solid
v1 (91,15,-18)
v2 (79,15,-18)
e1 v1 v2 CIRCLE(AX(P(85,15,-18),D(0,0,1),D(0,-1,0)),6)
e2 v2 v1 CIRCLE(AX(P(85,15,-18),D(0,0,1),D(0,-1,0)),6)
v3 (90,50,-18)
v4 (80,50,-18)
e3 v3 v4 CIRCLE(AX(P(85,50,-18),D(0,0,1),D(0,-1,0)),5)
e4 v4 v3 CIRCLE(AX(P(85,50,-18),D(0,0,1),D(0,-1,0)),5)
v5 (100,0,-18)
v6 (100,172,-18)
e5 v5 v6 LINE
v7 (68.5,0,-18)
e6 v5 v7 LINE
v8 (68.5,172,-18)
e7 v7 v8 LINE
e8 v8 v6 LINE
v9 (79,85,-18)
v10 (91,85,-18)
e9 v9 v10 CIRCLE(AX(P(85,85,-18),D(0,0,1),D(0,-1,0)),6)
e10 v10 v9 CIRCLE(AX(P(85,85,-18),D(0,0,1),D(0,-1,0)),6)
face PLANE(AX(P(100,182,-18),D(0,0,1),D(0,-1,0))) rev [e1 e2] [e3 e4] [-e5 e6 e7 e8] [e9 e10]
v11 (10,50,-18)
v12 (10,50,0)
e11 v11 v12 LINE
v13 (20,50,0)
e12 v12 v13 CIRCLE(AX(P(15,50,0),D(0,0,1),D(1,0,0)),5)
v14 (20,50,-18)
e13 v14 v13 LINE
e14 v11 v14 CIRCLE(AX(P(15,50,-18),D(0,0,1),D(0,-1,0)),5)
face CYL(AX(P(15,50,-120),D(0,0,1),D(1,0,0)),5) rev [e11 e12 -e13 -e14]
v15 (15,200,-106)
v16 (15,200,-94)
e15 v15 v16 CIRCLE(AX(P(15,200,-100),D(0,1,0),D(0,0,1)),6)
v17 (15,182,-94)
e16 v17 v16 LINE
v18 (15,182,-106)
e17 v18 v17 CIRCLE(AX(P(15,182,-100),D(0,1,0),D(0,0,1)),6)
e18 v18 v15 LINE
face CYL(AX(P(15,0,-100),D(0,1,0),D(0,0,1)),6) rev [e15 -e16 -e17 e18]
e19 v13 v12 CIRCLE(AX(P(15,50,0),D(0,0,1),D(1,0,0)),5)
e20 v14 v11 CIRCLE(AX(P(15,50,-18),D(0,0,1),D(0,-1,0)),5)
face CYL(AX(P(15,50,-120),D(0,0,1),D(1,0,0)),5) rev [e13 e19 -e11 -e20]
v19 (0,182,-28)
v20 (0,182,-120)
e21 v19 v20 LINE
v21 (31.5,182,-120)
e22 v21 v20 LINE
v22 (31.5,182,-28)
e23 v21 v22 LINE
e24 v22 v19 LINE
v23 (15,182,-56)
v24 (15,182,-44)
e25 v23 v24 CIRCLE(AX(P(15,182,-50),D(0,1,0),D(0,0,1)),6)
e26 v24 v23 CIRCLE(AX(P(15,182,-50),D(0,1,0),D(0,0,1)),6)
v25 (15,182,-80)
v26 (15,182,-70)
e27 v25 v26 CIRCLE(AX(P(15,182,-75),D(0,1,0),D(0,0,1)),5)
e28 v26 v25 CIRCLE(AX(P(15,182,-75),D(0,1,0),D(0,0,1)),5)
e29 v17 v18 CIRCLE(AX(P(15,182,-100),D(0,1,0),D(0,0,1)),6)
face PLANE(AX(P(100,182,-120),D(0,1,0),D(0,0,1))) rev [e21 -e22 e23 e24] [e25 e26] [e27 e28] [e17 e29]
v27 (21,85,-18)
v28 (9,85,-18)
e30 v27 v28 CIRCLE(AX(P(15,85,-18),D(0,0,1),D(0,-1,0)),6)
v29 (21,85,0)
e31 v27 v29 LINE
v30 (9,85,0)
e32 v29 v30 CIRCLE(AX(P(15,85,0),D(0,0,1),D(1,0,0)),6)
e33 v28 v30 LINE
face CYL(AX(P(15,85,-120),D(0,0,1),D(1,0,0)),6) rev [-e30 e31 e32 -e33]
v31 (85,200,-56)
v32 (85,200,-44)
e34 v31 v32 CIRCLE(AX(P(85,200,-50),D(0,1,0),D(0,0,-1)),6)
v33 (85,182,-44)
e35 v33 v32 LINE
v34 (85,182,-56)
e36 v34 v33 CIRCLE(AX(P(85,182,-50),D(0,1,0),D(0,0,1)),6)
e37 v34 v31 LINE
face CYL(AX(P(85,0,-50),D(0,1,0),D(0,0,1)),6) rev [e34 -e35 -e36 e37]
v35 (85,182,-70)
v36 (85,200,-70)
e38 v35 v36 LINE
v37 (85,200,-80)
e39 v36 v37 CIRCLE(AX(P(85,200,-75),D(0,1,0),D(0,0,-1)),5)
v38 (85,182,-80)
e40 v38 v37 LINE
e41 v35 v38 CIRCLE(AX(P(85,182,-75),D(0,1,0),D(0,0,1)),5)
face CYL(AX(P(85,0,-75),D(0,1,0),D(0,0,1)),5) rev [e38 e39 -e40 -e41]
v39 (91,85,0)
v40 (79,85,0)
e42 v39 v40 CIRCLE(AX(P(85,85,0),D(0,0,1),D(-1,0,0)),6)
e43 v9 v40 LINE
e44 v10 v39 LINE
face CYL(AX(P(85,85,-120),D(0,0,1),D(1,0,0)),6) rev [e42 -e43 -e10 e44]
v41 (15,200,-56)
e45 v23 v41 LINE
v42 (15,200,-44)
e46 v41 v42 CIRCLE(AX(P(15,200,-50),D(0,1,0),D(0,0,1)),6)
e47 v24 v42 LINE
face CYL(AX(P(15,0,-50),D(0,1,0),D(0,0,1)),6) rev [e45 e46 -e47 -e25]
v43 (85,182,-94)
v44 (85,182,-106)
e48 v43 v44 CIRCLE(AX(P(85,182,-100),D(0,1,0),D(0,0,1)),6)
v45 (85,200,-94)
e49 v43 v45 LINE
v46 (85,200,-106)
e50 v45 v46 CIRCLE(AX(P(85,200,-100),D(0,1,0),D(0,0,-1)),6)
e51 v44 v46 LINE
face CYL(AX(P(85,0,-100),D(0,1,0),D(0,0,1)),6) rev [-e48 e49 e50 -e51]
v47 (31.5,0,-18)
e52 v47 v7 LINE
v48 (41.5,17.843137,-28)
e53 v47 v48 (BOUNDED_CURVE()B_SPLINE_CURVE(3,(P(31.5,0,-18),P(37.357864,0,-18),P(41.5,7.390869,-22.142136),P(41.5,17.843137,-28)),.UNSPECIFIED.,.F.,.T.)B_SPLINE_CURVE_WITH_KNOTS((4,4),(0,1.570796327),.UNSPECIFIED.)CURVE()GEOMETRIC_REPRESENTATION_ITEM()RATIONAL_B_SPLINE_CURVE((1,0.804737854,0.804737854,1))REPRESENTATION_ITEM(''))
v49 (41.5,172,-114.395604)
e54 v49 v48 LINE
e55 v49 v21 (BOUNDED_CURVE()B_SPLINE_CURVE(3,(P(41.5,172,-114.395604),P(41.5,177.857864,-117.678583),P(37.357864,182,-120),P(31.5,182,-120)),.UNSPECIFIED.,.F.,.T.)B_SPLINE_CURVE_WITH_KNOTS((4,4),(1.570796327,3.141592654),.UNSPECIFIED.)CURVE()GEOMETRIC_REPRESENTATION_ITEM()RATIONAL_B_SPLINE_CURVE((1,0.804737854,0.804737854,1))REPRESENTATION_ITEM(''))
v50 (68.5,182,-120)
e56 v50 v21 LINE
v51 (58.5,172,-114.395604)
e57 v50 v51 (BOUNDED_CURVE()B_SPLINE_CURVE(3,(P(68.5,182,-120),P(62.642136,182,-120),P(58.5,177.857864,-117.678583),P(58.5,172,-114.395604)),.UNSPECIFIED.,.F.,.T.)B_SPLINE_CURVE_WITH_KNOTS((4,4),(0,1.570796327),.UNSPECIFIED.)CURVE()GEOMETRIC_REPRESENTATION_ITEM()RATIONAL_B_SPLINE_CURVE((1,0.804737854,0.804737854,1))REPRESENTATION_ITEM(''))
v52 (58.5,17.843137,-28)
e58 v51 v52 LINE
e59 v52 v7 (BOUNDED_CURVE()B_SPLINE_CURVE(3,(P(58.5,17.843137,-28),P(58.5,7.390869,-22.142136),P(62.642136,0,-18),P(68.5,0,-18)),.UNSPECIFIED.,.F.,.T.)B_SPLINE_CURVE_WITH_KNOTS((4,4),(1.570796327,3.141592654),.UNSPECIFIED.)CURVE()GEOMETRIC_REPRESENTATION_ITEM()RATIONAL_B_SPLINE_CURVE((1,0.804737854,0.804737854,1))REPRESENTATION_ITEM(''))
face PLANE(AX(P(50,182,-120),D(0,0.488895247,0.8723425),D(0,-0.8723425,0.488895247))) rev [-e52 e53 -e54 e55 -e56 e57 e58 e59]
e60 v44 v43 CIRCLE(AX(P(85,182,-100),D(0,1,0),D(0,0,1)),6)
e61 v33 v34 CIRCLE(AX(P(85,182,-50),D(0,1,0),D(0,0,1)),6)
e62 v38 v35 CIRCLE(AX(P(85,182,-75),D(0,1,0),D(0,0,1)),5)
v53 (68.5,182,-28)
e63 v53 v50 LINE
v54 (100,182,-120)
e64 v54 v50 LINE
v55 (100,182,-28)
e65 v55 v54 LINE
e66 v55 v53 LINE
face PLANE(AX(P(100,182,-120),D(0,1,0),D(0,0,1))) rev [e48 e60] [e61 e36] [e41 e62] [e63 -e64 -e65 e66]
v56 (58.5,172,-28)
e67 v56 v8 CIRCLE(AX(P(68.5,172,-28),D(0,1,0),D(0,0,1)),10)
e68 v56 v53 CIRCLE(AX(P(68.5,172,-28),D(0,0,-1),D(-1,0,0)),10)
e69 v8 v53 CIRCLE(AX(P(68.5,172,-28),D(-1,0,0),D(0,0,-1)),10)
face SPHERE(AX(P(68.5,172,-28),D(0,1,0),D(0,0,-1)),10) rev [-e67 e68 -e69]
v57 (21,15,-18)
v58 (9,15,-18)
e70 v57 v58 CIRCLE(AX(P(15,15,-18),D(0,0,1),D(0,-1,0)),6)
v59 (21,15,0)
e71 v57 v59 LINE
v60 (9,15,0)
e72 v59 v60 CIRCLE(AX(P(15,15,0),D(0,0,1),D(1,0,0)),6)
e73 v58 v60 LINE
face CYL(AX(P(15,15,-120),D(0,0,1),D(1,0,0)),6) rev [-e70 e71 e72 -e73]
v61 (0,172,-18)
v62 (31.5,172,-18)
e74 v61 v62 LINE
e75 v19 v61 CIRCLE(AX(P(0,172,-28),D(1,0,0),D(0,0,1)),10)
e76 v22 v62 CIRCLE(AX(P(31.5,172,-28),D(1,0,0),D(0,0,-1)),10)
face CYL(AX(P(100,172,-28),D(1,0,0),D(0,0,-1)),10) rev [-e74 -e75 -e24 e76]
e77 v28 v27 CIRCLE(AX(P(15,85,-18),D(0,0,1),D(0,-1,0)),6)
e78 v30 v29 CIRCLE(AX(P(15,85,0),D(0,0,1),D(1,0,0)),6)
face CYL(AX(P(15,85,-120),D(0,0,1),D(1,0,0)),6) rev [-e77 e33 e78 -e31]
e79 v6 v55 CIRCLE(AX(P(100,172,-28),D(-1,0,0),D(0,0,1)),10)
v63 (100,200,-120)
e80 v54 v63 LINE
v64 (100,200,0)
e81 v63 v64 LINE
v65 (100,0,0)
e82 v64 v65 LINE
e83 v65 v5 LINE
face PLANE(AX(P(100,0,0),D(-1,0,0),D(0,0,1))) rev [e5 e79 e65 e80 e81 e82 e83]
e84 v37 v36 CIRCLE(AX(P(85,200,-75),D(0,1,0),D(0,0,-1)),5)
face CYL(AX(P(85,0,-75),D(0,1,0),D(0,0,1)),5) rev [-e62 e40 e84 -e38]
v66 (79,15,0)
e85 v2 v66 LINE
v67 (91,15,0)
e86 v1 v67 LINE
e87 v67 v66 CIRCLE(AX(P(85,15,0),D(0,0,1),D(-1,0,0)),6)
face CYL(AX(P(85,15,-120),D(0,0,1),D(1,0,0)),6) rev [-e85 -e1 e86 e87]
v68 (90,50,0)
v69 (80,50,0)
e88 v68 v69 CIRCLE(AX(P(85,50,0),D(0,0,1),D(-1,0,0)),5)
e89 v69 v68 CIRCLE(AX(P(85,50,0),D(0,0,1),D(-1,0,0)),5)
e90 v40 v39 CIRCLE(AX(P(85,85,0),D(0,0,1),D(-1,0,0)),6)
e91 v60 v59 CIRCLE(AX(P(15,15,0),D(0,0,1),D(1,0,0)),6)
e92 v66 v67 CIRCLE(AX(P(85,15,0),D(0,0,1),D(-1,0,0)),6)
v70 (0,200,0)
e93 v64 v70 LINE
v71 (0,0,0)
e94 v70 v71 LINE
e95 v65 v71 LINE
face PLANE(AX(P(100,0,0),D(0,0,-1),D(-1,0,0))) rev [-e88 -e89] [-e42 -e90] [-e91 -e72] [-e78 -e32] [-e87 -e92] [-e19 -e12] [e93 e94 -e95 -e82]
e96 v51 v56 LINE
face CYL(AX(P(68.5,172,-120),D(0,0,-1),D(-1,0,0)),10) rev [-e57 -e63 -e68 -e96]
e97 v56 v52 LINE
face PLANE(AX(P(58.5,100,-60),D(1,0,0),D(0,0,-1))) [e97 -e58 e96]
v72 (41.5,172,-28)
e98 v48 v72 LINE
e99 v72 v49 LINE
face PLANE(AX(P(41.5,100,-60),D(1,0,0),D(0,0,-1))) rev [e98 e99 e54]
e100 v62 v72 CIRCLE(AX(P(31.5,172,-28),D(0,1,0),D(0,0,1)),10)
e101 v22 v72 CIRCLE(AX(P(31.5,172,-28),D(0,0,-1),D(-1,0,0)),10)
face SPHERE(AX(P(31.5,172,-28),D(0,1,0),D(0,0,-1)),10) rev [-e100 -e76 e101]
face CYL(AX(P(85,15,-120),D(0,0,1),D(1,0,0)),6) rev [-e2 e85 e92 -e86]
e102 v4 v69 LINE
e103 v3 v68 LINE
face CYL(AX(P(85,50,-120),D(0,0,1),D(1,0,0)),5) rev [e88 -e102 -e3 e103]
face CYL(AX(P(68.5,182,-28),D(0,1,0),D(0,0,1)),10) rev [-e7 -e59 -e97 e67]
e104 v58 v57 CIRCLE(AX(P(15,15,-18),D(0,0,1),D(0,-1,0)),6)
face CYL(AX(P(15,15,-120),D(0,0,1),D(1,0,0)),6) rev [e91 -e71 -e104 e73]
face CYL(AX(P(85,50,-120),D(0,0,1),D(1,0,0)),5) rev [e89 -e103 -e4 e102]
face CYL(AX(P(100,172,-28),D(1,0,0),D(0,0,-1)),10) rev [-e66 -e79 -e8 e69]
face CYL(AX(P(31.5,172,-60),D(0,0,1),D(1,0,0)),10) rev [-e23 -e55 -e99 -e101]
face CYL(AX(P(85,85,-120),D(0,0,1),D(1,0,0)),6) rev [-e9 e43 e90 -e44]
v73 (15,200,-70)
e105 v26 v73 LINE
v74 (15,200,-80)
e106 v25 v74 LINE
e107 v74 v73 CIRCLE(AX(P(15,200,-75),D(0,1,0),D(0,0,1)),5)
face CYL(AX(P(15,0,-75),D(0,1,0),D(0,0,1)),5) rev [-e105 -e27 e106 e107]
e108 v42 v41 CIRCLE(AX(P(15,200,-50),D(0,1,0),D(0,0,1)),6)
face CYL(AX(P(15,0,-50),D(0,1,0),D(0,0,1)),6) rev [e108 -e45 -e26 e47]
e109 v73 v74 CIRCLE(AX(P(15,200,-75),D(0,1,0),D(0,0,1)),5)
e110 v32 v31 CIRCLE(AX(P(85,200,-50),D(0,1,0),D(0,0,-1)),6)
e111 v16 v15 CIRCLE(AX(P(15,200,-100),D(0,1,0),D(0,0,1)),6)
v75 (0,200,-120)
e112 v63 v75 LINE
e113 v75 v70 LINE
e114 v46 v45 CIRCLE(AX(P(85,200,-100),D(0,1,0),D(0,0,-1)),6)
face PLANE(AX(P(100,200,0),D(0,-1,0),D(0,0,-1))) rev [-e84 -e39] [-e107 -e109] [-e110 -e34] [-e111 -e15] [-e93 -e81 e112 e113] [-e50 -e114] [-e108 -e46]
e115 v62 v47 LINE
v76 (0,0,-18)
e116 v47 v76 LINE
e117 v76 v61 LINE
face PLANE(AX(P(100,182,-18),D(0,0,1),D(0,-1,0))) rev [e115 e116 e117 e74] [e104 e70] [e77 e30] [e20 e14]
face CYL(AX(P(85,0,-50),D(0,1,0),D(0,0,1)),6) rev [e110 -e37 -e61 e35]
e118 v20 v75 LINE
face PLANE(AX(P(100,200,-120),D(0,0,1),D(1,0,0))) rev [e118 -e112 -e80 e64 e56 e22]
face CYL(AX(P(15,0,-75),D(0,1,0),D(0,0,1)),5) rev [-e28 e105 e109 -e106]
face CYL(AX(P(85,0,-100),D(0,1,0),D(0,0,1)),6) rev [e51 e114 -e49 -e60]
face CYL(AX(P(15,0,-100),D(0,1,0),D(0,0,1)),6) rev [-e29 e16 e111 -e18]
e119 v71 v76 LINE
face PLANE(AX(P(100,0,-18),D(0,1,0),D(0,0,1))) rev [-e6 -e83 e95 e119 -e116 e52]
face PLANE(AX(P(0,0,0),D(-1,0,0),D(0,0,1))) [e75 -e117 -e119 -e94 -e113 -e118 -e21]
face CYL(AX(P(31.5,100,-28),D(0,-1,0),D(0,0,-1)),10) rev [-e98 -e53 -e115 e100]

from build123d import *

# Parameters (mm, degrees)
BOSS_EXTRUDE1_DEPTH = 100
FILLET1_R           = 10
RIB3_REACH          = 240.537
SKETCH2_WALL_W      = 687.708067886
SKETCH2_WALL_H      = 17
FILLET2_R           = 10
SKETCH3_R           = 6
SKETCH3_R_2         = 5
CUT_EXTRUDE2_DEPTH  = 254.771550809
SKETCH7_R           = 6
SKETCH7_R_2         = 5
CUT_EXTRUDE3_DEPTH  = 254.771550809


with BuildPart() as part:
    # Sketch1 → Boss-Extrude1 (new body)
    with BuildSketch(Plane(origin=(0, 0, 0), x_dir=(0, 0, -1), z_dir=(1, 0, 0))):
        Polygon((0, 0), (0, 200), (120, 200), (120, 182), (18, 182), (18, 0), align=None)
    extrude(amount=BOSS_EXTRUDE1_DEPTH)

    # Fillet1
    fillet1_edges = [part.edges().sort_by_distance(p)[0] for p in [
        (50, 182, -18),
    ]]
    fillet(fillet1_edges, radius=FILLET1_R)

    # Sketch2 wall → Rib3 (add, up to next)
    with BuildSketch(Plane(origin=(50, 91, -69), x_dir=(0, -0.87234249996, 0.48889524723), z_dir=(0, -0.48889524723, -0.87234249996)), mode=Mode.PRIVATE) as rib3_sk1:
        Rectangle(SKETCH2_WALL_W, SKETCH2_WALL_H)
    rib3_tool1 = extrude(rib3_sk1.sketch, amount=-RIB3_REACH, mode=Mode.PRIVATE) - part.part
    add(rib3_tool1.solids().sort_by_distance((50, 91, -69))[0])

    # Fillet2
    fillet2_edges = [part.edges().sort_by_distance(p)[0] for p in [
        (41.5, 179.071067812, -20.928932188),
        (58.5, 179.071067812, -20.928932188),
        (41.5, 86, -18),
        (41.5, 182, -74),
        (58.5, 182, -74),
        (58.5, 86, -18),
    ]]
    fillet(fillet2_edges, radius=FILLET2_R)

    # Sketch3 → Cut-Extrude2 (cut, through all)
    with BuildSketch(Plane.XY):
        with Locations((15, 15)):
            Circle(SKETCH3_R)
        with Locations((15, 50)):
            Circle(SKETCH3_R_2)
        with Locations((15, 85)):
            Circle(SKETCH3_R)
        with Locations(Location((85, 15, 0), (0, 0, 270))):
            Circle(SKETCH3_R)
        with Locations(Location((85, 50, 0), (0, 0, 270))):
            Circle(SKETCH3_R_2)
        with Locations(Location((85, 85, 0), (0, 0, 270))):
            Circle(SKETCH3_R)
    extrude(amount=-CUT_EXTRUDE2_DEPTH, mode=Mode.SUBTRACT)

    # Sketch7 → Cut-Extrude3 (cut, through all)
    with BuildSketch(Plane(origin=(0, 200, 0), x_dir=(1, 0, 0), z_dir=(0, 1, 0))):
        with Locations(Location((15, 100, 0), (0, 0, 270))):
            Circle(SKETCH7_R)
        with Locations(Location((15, 75, 0), (0, 0, 270))):
            Circle(SKETCH7_R_2)
        with Locations(Location((15, 50, 0), (0, 0, 270))):
            Circle(SKETCH7_R)
        with Locations(Location((85, 50, 0), (0, 0, 270))):
            Circle(SKETCH7_R)
        with Locations(Location((85, 75, 0), (0, 0, 270))):
            Circle(SKETCH7_R_2)
        with Locations(Location((85, 100, 0), (0, 0, 270))):
            Circle(SKETCH7_R)
    extrude(amount=-CUT_EXTRUDE3_DEPTH, mode=Mode.SUBTRACT)


solid = part.part
